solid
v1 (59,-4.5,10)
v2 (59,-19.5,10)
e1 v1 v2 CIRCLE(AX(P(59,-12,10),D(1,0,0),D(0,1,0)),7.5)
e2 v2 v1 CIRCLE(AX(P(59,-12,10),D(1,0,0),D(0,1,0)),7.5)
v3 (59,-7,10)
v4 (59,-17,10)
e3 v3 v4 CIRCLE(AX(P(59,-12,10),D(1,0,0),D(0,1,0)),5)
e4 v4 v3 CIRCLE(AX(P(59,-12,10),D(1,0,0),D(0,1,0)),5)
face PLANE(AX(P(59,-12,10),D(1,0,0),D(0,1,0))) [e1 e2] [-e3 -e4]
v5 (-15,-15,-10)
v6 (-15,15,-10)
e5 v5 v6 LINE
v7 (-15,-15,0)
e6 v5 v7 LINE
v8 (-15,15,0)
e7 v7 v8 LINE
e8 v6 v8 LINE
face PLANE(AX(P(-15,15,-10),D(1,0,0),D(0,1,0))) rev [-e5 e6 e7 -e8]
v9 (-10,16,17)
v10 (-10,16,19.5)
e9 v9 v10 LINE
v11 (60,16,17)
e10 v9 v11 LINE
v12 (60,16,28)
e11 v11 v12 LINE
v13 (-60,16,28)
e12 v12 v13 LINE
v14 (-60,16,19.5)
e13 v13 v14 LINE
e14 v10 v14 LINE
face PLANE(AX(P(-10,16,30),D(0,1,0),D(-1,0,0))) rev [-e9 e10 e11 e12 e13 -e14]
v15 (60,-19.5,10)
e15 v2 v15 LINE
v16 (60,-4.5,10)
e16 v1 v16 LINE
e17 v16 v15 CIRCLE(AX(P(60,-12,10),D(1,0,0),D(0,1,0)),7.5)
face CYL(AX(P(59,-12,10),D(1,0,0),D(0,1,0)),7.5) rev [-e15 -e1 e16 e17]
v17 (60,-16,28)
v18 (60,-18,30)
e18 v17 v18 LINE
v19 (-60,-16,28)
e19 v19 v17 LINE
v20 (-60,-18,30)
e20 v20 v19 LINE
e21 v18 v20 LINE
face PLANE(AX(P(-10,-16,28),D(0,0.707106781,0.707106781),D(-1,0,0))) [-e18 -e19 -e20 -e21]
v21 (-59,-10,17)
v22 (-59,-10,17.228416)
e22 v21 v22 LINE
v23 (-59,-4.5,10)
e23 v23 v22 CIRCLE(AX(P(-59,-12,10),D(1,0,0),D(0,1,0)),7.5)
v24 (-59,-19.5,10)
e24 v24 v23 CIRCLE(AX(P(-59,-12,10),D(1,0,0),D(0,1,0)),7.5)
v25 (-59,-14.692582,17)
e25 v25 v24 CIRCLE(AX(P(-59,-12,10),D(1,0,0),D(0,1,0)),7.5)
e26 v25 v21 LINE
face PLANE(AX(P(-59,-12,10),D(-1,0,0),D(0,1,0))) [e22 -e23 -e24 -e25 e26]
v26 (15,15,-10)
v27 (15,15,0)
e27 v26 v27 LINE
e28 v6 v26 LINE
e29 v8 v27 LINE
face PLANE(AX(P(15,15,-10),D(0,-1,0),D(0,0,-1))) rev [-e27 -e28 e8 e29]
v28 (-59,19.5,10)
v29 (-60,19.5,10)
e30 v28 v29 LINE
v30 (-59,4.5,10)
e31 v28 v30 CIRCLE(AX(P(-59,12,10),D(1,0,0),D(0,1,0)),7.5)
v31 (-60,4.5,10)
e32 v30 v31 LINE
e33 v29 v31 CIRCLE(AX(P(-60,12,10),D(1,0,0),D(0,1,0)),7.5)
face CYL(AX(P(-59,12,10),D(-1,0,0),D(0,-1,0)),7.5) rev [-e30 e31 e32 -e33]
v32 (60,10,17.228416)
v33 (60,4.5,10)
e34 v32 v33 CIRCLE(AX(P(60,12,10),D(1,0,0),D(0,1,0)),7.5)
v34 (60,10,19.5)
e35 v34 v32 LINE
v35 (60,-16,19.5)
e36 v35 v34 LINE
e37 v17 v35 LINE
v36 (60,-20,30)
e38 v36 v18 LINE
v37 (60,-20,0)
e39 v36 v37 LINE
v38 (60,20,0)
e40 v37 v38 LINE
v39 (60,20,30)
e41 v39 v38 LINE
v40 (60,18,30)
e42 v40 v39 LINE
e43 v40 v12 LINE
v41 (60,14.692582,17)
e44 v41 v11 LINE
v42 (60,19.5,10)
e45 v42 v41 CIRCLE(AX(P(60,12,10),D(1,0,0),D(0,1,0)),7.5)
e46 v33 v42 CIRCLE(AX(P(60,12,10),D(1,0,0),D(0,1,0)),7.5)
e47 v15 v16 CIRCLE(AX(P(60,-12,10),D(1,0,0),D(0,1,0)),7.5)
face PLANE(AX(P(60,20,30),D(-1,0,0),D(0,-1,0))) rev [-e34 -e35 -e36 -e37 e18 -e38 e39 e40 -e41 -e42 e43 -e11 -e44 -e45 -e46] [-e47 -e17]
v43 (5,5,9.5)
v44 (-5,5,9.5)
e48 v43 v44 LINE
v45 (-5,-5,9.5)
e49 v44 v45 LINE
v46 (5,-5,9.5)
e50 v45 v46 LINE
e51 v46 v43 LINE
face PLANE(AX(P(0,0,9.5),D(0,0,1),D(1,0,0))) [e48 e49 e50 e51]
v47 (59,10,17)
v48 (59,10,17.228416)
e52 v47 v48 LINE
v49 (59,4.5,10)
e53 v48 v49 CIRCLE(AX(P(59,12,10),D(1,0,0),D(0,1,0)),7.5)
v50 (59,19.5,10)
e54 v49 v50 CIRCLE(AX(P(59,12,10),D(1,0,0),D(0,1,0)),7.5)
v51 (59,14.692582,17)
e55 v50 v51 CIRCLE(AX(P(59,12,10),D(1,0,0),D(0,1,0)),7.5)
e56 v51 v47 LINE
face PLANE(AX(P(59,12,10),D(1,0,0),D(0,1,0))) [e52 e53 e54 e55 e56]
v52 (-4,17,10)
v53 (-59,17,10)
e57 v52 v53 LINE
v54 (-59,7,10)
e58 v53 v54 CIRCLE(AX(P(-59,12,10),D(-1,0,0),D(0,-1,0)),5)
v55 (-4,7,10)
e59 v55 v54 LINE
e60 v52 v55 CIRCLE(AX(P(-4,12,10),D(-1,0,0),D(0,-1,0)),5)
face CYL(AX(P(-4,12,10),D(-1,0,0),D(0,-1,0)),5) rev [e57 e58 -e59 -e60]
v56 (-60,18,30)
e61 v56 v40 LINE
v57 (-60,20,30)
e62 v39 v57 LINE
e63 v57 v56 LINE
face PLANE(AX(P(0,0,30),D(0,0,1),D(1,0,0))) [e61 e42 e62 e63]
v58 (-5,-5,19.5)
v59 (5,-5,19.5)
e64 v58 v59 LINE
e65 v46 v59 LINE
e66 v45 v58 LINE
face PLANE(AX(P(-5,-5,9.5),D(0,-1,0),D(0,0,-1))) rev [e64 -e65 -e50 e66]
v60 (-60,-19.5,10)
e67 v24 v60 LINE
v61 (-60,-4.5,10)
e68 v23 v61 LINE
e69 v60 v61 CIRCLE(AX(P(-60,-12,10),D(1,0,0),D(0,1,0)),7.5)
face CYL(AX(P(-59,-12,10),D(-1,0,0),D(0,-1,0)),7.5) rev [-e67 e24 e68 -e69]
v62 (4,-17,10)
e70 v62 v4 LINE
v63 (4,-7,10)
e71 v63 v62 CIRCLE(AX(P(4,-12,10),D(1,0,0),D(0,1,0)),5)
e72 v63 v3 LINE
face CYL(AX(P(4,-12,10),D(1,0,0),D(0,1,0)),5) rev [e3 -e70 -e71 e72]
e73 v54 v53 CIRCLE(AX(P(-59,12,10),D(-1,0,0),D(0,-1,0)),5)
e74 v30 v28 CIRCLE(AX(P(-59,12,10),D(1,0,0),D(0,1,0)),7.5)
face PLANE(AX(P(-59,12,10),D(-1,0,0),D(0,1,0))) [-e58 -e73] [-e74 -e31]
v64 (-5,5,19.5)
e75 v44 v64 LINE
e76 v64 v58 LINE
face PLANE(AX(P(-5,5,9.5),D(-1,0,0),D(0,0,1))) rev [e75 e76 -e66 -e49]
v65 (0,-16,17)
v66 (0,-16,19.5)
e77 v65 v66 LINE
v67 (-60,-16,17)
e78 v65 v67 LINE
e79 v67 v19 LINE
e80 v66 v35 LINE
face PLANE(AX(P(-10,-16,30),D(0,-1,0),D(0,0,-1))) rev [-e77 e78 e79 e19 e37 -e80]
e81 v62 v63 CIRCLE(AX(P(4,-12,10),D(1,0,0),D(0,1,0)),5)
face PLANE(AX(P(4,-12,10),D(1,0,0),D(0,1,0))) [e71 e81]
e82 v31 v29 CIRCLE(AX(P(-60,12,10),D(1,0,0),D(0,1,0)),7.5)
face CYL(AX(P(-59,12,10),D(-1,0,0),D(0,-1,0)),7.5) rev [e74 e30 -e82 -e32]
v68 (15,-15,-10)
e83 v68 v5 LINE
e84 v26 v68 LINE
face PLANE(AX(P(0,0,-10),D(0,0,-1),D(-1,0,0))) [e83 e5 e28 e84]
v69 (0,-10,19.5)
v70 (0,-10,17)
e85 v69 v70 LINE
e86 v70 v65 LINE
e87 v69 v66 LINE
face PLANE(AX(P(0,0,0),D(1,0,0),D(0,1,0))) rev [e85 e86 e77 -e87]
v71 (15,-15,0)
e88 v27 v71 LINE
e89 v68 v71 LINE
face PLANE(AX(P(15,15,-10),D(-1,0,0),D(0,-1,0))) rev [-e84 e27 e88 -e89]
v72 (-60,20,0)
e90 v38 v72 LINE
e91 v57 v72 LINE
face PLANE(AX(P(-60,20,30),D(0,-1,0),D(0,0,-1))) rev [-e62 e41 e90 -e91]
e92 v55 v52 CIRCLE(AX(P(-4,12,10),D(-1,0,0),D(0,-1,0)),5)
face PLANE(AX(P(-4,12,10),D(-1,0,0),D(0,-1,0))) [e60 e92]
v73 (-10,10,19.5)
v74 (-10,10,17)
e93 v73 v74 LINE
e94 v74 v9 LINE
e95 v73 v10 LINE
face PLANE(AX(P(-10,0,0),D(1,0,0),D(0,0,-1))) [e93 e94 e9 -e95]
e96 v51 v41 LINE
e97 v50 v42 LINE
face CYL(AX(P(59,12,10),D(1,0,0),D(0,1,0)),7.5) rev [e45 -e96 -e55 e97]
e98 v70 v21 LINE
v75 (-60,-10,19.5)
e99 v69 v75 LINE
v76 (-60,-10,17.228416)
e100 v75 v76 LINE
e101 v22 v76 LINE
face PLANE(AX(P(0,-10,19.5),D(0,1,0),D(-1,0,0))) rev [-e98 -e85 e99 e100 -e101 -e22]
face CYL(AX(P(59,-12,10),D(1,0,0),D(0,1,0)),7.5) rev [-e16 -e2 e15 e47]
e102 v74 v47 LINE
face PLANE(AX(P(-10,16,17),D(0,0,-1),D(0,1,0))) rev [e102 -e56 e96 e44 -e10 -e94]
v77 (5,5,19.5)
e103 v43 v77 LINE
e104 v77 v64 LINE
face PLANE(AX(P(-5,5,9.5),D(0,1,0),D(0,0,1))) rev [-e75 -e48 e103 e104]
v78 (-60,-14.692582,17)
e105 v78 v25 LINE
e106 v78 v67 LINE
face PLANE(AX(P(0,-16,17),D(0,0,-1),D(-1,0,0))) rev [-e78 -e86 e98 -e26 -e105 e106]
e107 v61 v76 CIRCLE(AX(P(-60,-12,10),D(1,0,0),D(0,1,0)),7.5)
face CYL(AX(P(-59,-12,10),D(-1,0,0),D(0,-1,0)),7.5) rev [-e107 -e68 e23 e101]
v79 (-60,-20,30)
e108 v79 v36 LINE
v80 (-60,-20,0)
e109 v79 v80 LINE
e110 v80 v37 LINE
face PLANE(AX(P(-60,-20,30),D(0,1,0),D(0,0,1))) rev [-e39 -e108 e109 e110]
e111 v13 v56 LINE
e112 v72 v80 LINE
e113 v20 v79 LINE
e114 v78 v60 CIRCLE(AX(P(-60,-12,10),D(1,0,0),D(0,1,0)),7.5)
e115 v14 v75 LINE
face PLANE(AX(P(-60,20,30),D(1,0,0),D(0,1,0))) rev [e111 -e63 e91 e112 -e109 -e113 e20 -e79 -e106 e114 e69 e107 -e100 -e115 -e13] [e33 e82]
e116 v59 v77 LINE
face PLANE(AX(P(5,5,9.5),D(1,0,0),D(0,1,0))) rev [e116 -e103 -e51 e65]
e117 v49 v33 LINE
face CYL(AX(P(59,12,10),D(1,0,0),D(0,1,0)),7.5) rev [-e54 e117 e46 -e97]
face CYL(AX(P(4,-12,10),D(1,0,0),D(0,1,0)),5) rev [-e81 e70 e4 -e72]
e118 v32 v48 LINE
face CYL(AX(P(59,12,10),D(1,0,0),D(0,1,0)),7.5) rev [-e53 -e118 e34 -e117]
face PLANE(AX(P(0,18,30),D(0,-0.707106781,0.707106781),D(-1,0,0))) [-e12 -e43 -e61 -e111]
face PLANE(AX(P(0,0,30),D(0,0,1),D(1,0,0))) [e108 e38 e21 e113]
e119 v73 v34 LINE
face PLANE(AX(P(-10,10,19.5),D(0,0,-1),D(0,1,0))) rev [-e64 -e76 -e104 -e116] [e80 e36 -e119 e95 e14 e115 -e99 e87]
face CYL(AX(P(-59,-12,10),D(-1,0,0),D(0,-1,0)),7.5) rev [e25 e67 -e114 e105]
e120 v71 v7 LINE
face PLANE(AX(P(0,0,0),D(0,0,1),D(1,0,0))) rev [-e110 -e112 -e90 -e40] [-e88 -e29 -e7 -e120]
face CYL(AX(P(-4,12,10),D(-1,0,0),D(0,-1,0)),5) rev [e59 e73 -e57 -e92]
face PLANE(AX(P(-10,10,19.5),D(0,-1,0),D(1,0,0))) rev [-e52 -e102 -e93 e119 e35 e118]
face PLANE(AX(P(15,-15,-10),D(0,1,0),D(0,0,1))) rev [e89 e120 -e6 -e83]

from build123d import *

# Parameters (mm, degrees)
SKETCH1_W           = 120
SKETCH1_H           = 40
BOSS_EXTRUDE1_DEPTH = 30
CUT_EXTRUDE1_DEPTH  = 70
CUT_EXTRUDE2_DEPTH  = 60
SKETCH5_W           = 30
SKETCH5_H           = 30
BOSS_EXTRUDE2_DEPTH = 10
SKETCH7_W           = 10
SKETCH7_H           = 10
CUT_EXTRUDE4_DEPTH  = 10
CHAMFER1_SIZE       = 2
SKETCH6_R           = 7.5
CUT_EXTRUDE5_DEPTH  = 1
SKETCH9_R           = 5
CUT_EXTRUDE6_DEPTH  = 55
SKETCH10_R          = 5
CUT_EXTRUDE7_DEPTH  = 55


with BuildPart() as part:
    # Sketch1 → Boss-Extrude1 (new body)
    with BuildSketch(Plane.XY):
        Rectangle(SKETCH1_W, SKETCH1_H)
    extrude(amount=BOSS_EXTRUDE1_DEPTH)

    # Sketch3 → Cut-Extrude1 (cut)
    with BuildSketch(Plane(origin=(60, 0, 0), x_dir=(0, 0, -1), z_dir=(1, 0, 0))):
        Polygon((-30, 16), (-17, 16), (-17, 10), (-19.5, 10), (-19.5, -16), (-30, -16), align=None)
    extrude(amount=-CUT_EXTRUDE1_DEPTH, mode=Mode.SUBTRACT)

    # Sketch4 → Cut-Extrude2 (cut)
    with BuildSketch(Plane.ZY.offset(60)):
        Polygon((30, 16), (19.5, 16), (19.5, -10), (17, -10), (17, -16), (30, -16), align=None)
    extrude(amount=-CUT_EXTRUDE2_DEPTH, mode=Mode.SUBTRACT)

    # Sketch5 → Boss-Extrude2 (add)
    with BuildSketch(Plane(origin=(0, 0, 0), x_dir=(-1, 0, 0), z_dir=(0, 0, -1))):
        Rectangle(SKETCH5_W, SKETCH5_H)
    extrude(amount=BOSS_EXTRUDE2_DEPTH)

    # Sketch7 → Cut-Extrude4 (cut)
    with BuildSketch(Plane.XY.offset(19.5)):
        Rectangle(SKETCH7_W, SKETCH7_H)
    extrude(amount=-CUT_EXTRUDE4_DEPTH, mode=Mode.SUBTRACT)

    # Chamfer1
    chamfer1_edges = [part.edges().sort_by_distance(p)[0] for p in [
        (0, -16, 30),
        (0, 16, 30),
    ]]
    chamfer(chamfer1_edges, length=CHAMFER1_SIZE)

    # Sketch6 → Cut-Extrude5 (cut)
    with BuildSketch(Plane(origin=(60, 0, 0), x_dir=(0, 0, -1), z_dir=(1, 0, 0))):
        with Locations((-10, 12)):
            Circle(SKETCH6_R)
        with Locations(Location((-10, -12, 0), (0, 0, 90))):
            Circle(SKETCH6_R)
    cut_extrude5 = extrude(amount=-CUT_EXTRUDE5_DEPTH, mode=Mode.SUBTRACT)

    # Sketch9 → Cut-Extrude6 (cut)
    with BuildSketch(Plane(origin=(59, 0, 0), x_dir=(0, 0, -1), z_dir=(1, 0, 0))):
        with Locations(Location((-10, -12, 0), (0, 0, 90))):
            Circle(SKETCH9_R)
    extrude(amount=-CUT_EXTRUDE6_DEPTH, mode=Mode.SUBTRACT)

    # Mirror1: Cut-Extrude5 across plane
    add(cut_extrude5.mirror(Plane(origin=(0, 0, 0), x_dir=(0, 0, 1), z_dir=(1, 0, 0))), mode=Mode.SUBTRACT)

    # Sketch10 → Cut-Extrude7 (cut)
    with BuildSketch(Plane.ZY.offset(59)):
        with Locations(Location((10, 12, 0), (0, 0, 270))):
            Circle(SKETCH10_R)
    extrude(amount=-CUT_EXTRUDE7_DEPTH, mode=Mode.SUBTRACT)


solid = part.part
